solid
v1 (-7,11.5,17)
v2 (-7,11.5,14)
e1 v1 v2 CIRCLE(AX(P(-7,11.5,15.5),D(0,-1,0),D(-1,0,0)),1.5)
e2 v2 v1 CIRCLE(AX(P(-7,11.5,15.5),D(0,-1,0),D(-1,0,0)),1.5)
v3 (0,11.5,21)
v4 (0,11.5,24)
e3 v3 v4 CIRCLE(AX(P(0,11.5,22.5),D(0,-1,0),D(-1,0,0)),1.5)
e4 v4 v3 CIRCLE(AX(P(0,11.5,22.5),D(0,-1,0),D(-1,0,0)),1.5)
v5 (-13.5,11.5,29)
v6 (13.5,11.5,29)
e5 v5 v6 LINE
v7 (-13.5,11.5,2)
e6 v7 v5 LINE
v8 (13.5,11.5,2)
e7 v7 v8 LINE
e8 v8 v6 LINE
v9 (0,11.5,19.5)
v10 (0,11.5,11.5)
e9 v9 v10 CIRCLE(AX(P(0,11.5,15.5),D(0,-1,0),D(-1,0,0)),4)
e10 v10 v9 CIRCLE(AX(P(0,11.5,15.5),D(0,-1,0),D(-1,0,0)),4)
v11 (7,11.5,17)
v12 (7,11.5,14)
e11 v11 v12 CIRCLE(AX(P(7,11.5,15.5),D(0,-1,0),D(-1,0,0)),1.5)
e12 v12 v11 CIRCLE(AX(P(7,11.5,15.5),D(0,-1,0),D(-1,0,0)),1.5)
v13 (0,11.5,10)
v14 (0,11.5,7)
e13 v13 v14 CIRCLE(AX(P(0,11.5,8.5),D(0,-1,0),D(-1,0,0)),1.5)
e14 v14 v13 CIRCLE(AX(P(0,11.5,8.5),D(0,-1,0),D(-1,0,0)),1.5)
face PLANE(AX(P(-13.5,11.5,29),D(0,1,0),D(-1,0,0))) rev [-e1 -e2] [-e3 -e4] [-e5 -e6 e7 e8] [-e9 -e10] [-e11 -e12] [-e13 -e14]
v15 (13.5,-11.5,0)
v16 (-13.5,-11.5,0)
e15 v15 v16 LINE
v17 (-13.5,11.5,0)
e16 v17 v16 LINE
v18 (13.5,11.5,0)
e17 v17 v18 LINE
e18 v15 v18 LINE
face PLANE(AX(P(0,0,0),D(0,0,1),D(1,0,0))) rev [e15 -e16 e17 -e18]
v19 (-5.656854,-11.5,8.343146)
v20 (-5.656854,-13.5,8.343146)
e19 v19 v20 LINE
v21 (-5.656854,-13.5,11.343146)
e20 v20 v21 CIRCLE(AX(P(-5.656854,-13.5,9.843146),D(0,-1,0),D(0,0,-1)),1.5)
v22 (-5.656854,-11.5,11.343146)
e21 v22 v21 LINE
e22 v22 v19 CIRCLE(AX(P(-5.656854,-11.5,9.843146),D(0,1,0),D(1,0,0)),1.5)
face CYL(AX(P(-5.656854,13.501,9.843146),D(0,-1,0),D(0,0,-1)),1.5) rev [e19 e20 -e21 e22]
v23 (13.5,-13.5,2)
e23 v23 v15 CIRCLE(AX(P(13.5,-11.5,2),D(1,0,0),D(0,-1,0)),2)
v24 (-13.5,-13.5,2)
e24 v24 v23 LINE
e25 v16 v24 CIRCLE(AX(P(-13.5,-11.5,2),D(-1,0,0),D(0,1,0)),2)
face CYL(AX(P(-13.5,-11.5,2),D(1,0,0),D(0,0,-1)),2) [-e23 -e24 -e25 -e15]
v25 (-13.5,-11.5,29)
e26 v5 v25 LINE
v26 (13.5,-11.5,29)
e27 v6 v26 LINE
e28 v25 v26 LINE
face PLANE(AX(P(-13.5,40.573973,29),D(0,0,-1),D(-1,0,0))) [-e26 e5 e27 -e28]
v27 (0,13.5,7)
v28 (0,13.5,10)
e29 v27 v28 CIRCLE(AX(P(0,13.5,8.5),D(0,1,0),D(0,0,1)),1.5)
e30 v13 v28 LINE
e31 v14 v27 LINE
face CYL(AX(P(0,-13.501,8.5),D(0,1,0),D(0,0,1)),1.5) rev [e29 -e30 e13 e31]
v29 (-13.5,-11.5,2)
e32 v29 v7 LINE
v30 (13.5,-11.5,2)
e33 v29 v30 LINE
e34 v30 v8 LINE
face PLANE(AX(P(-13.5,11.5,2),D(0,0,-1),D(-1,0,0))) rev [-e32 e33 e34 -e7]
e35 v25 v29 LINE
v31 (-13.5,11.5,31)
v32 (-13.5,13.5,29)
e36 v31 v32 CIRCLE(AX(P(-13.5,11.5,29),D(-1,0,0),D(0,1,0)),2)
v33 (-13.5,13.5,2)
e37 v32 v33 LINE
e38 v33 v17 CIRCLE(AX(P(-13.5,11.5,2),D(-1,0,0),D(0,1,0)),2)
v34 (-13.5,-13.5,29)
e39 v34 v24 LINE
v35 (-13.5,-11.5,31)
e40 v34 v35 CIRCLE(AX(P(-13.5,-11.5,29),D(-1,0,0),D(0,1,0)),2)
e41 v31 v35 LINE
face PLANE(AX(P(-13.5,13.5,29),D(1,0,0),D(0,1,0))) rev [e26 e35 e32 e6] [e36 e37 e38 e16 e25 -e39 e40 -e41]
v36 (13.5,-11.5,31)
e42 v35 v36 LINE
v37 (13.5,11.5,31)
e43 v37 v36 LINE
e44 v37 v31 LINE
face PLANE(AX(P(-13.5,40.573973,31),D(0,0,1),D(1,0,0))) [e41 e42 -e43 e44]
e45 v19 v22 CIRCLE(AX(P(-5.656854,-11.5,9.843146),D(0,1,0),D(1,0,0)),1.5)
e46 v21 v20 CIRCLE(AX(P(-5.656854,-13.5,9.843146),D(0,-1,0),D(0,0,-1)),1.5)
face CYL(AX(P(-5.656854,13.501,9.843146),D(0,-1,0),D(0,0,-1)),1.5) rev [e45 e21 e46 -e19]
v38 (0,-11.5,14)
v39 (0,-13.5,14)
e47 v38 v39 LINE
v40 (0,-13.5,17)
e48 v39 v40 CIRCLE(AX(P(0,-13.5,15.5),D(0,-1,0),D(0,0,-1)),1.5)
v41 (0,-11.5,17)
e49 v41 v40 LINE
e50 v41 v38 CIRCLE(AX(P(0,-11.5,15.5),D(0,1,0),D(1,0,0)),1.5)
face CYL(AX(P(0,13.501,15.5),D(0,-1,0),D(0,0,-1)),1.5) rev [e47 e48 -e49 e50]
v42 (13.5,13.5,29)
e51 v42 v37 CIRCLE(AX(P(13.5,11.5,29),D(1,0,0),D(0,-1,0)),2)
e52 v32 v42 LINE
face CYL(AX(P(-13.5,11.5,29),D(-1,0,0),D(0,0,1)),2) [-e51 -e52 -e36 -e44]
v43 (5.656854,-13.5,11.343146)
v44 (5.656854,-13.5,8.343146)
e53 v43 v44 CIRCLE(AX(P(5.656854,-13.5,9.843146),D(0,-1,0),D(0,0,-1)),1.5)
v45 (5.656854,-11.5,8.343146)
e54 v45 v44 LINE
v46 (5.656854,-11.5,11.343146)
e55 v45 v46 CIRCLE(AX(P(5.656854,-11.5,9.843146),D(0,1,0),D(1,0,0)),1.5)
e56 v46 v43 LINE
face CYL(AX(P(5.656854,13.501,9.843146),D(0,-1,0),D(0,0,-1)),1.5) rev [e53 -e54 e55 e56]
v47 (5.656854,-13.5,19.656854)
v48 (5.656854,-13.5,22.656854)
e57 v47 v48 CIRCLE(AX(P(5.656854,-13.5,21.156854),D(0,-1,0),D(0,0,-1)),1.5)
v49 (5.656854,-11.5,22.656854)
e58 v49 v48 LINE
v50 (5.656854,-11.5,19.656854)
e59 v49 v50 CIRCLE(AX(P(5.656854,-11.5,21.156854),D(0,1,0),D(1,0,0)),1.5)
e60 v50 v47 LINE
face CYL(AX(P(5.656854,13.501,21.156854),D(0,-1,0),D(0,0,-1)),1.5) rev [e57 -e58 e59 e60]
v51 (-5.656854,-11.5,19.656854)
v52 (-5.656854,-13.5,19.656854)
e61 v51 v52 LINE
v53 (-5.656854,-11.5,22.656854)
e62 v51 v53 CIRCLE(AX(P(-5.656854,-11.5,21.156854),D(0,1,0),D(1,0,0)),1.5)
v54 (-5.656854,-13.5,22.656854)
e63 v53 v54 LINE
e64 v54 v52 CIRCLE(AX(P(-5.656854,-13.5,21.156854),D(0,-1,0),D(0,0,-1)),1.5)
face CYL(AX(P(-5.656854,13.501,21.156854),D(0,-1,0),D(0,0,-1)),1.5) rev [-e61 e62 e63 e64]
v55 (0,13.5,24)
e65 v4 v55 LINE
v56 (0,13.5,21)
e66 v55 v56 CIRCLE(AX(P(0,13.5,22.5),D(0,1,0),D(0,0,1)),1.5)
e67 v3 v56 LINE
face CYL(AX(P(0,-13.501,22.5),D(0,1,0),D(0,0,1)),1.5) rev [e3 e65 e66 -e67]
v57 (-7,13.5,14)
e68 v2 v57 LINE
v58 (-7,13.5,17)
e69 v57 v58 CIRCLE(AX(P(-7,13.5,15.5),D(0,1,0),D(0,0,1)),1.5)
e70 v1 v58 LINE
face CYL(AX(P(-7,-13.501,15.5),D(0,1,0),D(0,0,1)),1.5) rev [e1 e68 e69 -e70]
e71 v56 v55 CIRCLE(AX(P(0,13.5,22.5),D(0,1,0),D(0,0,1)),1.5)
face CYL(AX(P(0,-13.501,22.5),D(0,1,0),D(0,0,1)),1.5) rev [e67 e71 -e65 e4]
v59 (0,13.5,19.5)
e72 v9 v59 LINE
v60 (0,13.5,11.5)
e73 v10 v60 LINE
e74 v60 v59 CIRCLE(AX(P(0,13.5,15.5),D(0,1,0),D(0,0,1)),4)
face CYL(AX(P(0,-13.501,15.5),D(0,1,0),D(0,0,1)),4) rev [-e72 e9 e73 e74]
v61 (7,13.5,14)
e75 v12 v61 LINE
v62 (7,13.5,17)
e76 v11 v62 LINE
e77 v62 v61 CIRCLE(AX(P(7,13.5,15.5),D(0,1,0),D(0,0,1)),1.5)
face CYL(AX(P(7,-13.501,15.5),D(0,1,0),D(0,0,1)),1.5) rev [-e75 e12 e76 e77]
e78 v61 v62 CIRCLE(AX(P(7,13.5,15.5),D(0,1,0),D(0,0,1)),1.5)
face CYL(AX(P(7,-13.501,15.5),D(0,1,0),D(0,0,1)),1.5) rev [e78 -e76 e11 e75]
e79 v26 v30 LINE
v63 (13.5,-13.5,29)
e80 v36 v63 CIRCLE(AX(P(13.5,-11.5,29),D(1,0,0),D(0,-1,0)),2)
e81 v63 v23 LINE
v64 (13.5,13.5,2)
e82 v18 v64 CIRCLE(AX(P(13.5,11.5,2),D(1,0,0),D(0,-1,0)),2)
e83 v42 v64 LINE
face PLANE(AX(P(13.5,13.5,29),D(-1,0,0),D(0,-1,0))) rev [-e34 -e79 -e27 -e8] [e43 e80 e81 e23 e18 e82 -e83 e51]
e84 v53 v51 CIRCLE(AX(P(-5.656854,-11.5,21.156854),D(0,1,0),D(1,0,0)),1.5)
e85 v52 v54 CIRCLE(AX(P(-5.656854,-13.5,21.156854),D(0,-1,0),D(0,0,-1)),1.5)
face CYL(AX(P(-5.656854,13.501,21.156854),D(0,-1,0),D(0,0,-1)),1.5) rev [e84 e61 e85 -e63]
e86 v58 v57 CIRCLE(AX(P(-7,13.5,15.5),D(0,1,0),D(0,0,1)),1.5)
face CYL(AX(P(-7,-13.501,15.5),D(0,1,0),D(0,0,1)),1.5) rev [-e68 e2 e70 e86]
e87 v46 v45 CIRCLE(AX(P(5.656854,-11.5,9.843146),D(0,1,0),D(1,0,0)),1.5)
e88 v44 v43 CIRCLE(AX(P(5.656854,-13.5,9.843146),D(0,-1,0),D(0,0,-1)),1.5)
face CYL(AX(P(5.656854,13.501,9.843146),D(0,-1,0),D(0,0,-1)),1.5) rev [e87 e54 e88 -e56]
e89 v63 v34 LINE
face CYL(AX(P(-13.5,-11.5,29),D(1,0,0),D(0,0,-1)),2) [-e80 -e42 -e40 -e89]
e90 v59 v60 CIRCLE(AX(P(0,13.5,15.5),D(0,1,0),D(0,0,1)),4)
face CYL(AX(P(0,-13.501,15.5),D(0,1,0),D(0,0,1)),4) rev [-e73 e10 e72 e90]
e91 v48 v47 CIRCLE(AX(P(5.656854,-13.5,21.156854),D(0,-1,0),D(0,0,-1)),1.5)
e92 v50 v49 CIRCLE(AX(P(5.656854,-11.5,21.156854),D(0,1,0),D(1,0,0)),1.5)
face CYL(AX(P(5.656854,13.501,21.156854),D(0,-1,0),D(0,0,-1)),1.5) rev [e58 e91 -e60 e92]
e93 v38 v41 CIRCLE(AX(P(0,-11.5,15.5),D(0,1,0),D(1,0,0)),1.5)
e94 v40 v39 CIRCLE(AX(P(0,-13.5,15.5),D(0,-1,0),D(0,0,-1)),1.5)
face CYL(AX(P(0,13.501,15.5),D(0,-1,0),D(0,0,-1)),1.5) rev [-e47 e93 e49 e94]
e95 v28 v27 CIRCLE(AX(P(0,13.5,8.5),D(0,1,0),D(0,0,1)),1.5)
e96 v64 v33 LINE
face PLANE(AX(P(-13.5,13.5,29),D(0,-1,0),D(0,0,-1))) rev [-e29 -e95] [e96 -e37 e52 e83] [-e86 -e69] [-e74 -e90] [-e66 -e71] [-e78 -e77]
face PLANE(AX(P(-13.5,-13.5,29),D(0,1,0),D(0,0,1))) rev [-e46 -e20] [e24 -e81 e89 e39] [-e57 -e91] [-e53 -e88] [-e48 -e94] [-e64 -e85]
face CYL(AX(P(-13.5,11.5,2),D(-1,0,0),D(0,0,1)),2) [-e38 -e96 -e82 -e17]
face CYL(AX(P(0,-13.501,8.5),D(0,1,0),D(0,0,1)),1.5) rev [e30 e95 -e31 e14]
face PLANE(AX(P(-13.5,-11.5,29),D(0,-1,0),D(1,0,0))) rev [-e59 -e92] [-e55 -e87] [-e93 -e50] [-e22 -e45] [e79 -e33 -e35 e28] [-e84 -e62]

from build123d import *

# Parameters (mm, degrees)
SKETCH1_W           = 27
SKETCH1_H           = 27
BOSS_EXTRUDE1_DEPTH = 29
SKETCH2_W           = 27
SKETCH2_H           = 23
CUT_EXTRUDE1_DEPTH  = 27
CUT_EXTRUDE2_REACH  = 43.86
SKETCH4_R           = 4
SKETCH4_R_2         = 1.5
CUT_EXTRUDE3_REACH  = 43.86
SKETCH5_R           = 1.5
FILLET1_R           = 2
SKETCH6_W           = 27
SKETCH6_H           = 2
BOSS_EXTRUDE2_DEPTH = 27
FILLET2_R           = 2


with BuildPart() as part:
    # Sketch1 → Boss-Extrude1 (new body)
    with BuildSketch(Plane.XY):
        Rectangle(SKETCH1_W, SKETCH1_H)
    extrude(amount=BOSS_EXTRUDE1_DEPTH)

    # Sketch2 → Cut-Extrude1 (cut)
    with BuildSketch(Plane(origin=(13.5, 0, 0), x_dir=(0, 0, -1), z_dir=(1, 0, 0))):
        with Locations((-15.5, 0)):
            Rectangle(SKETCH2_W, SKETCH2_H)
    extrude(amount=-CUT_EXTRUDE1_DEPTH, mode=Mode.SUBTRACT)

    # Sketch4 → Cut-Extrude2 (cut, up to next)
    with BuildSketch(Plane(origin=(0, 13.5, 0), x_dir=(1, 0, 0), z_dir=(0, 1, 0)), mode=Mode.PRIVATE) as cut_extrude2_sk1:
        with Locations(Location((0, -15.5, 0), (0, 0, 270))):
            Circle(SKETCH4_R)
    cut_extrude2_tool1 = extrude(cut_extrude2_sk1.sketch, amount=-CUT_EXTRUDE2_REACH, mode=Mode.PRIVATE) & part.part
    # Sketch4 → Cut-Extrude2 (cut, up to next)
    with BuildSketch(Plane(origin=(0, 13.5, 0), x_dir=(1, 0, 0), z_dir=(0, 1, 0)), mode=Mode.PRIVATE) as cut_extrude2_sk2:
        with Locations(Location((0, -8.5, 0), (0, 0, 270))):
            Circle(SKETCH4_R_2)
    cut_extrude2_tool2 = extrude(cut_extrude2_sk2.sketch, amount=-CUT_EXTRUDE2_REACH, mode=Mode.PRIVATE) & part.part
    # Sketch4 → Cut-Extrude2 (cut, up to next)
    with BuildSketch(Plane(origin=(0, 13.5, 0), x_dir=(1, 0, 0), z_dir=(0, 1, 0)), mode=Mode.PRIVATE) as cut_extrude2_sk3:
        with Locations(Location((7, -15.5, 0), (0, 0, 270))):
            Circle(SKETCH4_R_2)
    cut_extrude2_tool3 = extrude(cut_extrude2_sk3.sketch, amount=-CUT_EXTRUDE2_REACH, mode=Mode.PRIVATE) & part.part
    # Sketch4 → Cut-Extrude2 (cut, up to next)
    with BuildSketch(Plane(origin=(0, 13.5, 0), x_dir=(1, 0, 0), z_dir=(0, 1, 0)), mode=Mode.PRIVATE) as cut_extrude2_sk4:
        with Locations(Location((0, -22.5, 0), (0, 0, 270))):
            Circle(SKETCH4_R_2)
    cut_extrude2_tool4 = extrude(cut_extrude2_sk4.sketch, amount=-CUT_EXTRUDE2_REACH, mode=Mode.PRIVATE) & part.part
    # Sketch4 → Cut-Extrude2 (cut, up to next)
    with BuildSketch(Plane(origin=(0, 13.5, 0), x_dir=(1, 0, 0), z_dir=(0, 1, 0)), mode=Mode.PRIVATE) as cut_extrude2_sk5:
        with Locations(Location((-7, -15.5, 0), (0, 0, 270))):
            Circle(SKETCH4_R_2)
    cut_extrude2_tool5 = extrude(cut_extrude2_sk5.sketch, amount=-CUT_EXTRUDE2_REACH, mode=Mode.PRIVATE) & part.part
    add(cut_extrude2_tool1.solids().sort_by_distance((0, 13.5, 15.5))[0], mode=Mode.SUBTRACT)
    add(cut_extrude2_tool2.solids().sort_by_distance((0, 13.5, 8.5))[0], mode=Mode.SUBTRACT)
    add(cut_extrude2_tool3.solids().sort_by_distance((7, 13.5, 15.5))[0], mode=Mode.SUBTRACT)
    add(cut_extrude2_tool4.solids().sort_by_distance((0, 13.5, 22.5))[0], mode=Mode.SUBTRACT)
    add(cut_extrude2_tool5.solids().sort_by_distance((-7, 13.5, 15.5))[0], mode=Mode.SUBTRACT)

    # Sketch5 → Cut-Extrude3 (cut, up to next)
    with BuildSketch(Plane.XZ.offset(13.5), mode=Mode.PRIVATE) as cut_extrude3_sk1:
        with Locations(Location((0, 15.5, 0), (0, 0, 270))):
            Circle(SKETCH5_R)
    cut_extrude3_tool1 = extrude(cut_extrude3_sk1.sketch, amount=-CUT_EXTRUDE3_REACH, mode=Mode.PRIVATE) & part.part
    # Sketch5 → Cut-Extrude3 (cut, up to next)
    with BuildSketch(Plane.XZ.offset(13.5), mode=Mode.PRIVATE) as cut_extrude3_sk2:
        with Locations(Location((-5.656854249, 21.156854249, 0), (0, 0, 270))):
            Circle(SKETCH5_R)
    cut_extrude3_tool2 = extrude(cut_extrude3_sk2.sketch, amount=-CUT_EXTRUDE3_REACH, mode=Mode.PRIVATE) & part.part
    # Sketch5 → Cut-Extrude3 (cut, up to next)
    with BuildSketch(Plane.XZ.offset(13.5), mode=Mode.PRIVATE) as cut_extrude3_sk3:
        with Locations(Location((5.656854249, 21.156854249, 0), (0, 0, 270))):
            Circle(SKETCH5_R)
    cut_extrude3_tool3 = extrude(cut_extrude3_sk3.sketch, amount=-CUT_EXTRUDE3_REACH, mode=Mode.PRIVATE) & part.part
    # Sketch5 → Cut-Extrude3 (cut, up to next)
    with BuildSketch(Plane.XZ.offset(13.5), mode=Mode.PRIVATE) as cut_extrude3_sk4:
        with Locations(Location((5.656854249, 9.843145751, 0), (0, 0, 270))):
            Circle(SKETCH5_R)
    cut_extrude3_tool4 = extrude(cut_extrude3_sk4.sketch, amount=-CUT_EXTRUDE3_REACH, mode=Mode.PRIVATE) & part.part
    # Sketch5 → Cut-Extrude3 (cut, up to next)
    with BuildSketch(Plane.XZ.offset(13.5), mode=Mode.PRIVATE) as cut_extrude3_sk5:
        with Locations(Location((-5.656854249, 9.843145751, 0), (0, 0, 270))):
            Circle(SKETCH5_R)
    cut_extrude3_tool5 = extrude(cut_extrude3_sk5.sketch, amount=-CUT_EXTRUDE3_REACH, mode=Mode.PRIVATE) & part.part
    add(cut_extrude3_tool1.solids().sort_by_distance((0, -13.5, 15.5))[0], mode=Mode.SUBTRACT)
    add(cut_extrude3_tool2.solids().sort_by_distance((-5.656854, -13.5, 21.156854))[0], mode=Mode.SUBTRACT)
    add(cut_extrude3_tool3.solids().sort_by_distance((5.656854, -13.5, 21.156854))[0], mode=Mode.SUBTRACT)
    add(cut_extrude3_tool4.solids().sort_by_distance((5.656854, -13.5, 9.843146))[0], mode=Mode.SUBTRACT)
    add(cut_extrude3_tool5.solids().sort_by_distance((-5.656854, -13.5, 9.843146))[0], mode=Mode.SUBTRACT)

    # Fillet1
    fillet1_edges = [part.edges().sort_by_distance(p)[0] for p in [
        (0, -13.5, 0),
        (0, 13.5, 0),
    ]]
    fillet(fillet1_edges, radius=FILLET1_R)

    # Sketch6 → Boss-Extrude2 (add)
    with BuildSketch(Plane.XZ.offset(13.5)):
        with Locations((0, 30)):
            Rectangle(SKETCH6_W, SKETCH6_H)
    extrude(amount=-BOSS_EXTRUDE2_DEPTH)

    # Fillet2
    fillet2_edges = [part.edges().sort_by_distance(p)[0] for p in [
        (0, -13.5, 31),
        (0, 13.5, 31),
    ]]
    fillet(fillet2_edges, radius=FILLET2_R)


solid = part.part
